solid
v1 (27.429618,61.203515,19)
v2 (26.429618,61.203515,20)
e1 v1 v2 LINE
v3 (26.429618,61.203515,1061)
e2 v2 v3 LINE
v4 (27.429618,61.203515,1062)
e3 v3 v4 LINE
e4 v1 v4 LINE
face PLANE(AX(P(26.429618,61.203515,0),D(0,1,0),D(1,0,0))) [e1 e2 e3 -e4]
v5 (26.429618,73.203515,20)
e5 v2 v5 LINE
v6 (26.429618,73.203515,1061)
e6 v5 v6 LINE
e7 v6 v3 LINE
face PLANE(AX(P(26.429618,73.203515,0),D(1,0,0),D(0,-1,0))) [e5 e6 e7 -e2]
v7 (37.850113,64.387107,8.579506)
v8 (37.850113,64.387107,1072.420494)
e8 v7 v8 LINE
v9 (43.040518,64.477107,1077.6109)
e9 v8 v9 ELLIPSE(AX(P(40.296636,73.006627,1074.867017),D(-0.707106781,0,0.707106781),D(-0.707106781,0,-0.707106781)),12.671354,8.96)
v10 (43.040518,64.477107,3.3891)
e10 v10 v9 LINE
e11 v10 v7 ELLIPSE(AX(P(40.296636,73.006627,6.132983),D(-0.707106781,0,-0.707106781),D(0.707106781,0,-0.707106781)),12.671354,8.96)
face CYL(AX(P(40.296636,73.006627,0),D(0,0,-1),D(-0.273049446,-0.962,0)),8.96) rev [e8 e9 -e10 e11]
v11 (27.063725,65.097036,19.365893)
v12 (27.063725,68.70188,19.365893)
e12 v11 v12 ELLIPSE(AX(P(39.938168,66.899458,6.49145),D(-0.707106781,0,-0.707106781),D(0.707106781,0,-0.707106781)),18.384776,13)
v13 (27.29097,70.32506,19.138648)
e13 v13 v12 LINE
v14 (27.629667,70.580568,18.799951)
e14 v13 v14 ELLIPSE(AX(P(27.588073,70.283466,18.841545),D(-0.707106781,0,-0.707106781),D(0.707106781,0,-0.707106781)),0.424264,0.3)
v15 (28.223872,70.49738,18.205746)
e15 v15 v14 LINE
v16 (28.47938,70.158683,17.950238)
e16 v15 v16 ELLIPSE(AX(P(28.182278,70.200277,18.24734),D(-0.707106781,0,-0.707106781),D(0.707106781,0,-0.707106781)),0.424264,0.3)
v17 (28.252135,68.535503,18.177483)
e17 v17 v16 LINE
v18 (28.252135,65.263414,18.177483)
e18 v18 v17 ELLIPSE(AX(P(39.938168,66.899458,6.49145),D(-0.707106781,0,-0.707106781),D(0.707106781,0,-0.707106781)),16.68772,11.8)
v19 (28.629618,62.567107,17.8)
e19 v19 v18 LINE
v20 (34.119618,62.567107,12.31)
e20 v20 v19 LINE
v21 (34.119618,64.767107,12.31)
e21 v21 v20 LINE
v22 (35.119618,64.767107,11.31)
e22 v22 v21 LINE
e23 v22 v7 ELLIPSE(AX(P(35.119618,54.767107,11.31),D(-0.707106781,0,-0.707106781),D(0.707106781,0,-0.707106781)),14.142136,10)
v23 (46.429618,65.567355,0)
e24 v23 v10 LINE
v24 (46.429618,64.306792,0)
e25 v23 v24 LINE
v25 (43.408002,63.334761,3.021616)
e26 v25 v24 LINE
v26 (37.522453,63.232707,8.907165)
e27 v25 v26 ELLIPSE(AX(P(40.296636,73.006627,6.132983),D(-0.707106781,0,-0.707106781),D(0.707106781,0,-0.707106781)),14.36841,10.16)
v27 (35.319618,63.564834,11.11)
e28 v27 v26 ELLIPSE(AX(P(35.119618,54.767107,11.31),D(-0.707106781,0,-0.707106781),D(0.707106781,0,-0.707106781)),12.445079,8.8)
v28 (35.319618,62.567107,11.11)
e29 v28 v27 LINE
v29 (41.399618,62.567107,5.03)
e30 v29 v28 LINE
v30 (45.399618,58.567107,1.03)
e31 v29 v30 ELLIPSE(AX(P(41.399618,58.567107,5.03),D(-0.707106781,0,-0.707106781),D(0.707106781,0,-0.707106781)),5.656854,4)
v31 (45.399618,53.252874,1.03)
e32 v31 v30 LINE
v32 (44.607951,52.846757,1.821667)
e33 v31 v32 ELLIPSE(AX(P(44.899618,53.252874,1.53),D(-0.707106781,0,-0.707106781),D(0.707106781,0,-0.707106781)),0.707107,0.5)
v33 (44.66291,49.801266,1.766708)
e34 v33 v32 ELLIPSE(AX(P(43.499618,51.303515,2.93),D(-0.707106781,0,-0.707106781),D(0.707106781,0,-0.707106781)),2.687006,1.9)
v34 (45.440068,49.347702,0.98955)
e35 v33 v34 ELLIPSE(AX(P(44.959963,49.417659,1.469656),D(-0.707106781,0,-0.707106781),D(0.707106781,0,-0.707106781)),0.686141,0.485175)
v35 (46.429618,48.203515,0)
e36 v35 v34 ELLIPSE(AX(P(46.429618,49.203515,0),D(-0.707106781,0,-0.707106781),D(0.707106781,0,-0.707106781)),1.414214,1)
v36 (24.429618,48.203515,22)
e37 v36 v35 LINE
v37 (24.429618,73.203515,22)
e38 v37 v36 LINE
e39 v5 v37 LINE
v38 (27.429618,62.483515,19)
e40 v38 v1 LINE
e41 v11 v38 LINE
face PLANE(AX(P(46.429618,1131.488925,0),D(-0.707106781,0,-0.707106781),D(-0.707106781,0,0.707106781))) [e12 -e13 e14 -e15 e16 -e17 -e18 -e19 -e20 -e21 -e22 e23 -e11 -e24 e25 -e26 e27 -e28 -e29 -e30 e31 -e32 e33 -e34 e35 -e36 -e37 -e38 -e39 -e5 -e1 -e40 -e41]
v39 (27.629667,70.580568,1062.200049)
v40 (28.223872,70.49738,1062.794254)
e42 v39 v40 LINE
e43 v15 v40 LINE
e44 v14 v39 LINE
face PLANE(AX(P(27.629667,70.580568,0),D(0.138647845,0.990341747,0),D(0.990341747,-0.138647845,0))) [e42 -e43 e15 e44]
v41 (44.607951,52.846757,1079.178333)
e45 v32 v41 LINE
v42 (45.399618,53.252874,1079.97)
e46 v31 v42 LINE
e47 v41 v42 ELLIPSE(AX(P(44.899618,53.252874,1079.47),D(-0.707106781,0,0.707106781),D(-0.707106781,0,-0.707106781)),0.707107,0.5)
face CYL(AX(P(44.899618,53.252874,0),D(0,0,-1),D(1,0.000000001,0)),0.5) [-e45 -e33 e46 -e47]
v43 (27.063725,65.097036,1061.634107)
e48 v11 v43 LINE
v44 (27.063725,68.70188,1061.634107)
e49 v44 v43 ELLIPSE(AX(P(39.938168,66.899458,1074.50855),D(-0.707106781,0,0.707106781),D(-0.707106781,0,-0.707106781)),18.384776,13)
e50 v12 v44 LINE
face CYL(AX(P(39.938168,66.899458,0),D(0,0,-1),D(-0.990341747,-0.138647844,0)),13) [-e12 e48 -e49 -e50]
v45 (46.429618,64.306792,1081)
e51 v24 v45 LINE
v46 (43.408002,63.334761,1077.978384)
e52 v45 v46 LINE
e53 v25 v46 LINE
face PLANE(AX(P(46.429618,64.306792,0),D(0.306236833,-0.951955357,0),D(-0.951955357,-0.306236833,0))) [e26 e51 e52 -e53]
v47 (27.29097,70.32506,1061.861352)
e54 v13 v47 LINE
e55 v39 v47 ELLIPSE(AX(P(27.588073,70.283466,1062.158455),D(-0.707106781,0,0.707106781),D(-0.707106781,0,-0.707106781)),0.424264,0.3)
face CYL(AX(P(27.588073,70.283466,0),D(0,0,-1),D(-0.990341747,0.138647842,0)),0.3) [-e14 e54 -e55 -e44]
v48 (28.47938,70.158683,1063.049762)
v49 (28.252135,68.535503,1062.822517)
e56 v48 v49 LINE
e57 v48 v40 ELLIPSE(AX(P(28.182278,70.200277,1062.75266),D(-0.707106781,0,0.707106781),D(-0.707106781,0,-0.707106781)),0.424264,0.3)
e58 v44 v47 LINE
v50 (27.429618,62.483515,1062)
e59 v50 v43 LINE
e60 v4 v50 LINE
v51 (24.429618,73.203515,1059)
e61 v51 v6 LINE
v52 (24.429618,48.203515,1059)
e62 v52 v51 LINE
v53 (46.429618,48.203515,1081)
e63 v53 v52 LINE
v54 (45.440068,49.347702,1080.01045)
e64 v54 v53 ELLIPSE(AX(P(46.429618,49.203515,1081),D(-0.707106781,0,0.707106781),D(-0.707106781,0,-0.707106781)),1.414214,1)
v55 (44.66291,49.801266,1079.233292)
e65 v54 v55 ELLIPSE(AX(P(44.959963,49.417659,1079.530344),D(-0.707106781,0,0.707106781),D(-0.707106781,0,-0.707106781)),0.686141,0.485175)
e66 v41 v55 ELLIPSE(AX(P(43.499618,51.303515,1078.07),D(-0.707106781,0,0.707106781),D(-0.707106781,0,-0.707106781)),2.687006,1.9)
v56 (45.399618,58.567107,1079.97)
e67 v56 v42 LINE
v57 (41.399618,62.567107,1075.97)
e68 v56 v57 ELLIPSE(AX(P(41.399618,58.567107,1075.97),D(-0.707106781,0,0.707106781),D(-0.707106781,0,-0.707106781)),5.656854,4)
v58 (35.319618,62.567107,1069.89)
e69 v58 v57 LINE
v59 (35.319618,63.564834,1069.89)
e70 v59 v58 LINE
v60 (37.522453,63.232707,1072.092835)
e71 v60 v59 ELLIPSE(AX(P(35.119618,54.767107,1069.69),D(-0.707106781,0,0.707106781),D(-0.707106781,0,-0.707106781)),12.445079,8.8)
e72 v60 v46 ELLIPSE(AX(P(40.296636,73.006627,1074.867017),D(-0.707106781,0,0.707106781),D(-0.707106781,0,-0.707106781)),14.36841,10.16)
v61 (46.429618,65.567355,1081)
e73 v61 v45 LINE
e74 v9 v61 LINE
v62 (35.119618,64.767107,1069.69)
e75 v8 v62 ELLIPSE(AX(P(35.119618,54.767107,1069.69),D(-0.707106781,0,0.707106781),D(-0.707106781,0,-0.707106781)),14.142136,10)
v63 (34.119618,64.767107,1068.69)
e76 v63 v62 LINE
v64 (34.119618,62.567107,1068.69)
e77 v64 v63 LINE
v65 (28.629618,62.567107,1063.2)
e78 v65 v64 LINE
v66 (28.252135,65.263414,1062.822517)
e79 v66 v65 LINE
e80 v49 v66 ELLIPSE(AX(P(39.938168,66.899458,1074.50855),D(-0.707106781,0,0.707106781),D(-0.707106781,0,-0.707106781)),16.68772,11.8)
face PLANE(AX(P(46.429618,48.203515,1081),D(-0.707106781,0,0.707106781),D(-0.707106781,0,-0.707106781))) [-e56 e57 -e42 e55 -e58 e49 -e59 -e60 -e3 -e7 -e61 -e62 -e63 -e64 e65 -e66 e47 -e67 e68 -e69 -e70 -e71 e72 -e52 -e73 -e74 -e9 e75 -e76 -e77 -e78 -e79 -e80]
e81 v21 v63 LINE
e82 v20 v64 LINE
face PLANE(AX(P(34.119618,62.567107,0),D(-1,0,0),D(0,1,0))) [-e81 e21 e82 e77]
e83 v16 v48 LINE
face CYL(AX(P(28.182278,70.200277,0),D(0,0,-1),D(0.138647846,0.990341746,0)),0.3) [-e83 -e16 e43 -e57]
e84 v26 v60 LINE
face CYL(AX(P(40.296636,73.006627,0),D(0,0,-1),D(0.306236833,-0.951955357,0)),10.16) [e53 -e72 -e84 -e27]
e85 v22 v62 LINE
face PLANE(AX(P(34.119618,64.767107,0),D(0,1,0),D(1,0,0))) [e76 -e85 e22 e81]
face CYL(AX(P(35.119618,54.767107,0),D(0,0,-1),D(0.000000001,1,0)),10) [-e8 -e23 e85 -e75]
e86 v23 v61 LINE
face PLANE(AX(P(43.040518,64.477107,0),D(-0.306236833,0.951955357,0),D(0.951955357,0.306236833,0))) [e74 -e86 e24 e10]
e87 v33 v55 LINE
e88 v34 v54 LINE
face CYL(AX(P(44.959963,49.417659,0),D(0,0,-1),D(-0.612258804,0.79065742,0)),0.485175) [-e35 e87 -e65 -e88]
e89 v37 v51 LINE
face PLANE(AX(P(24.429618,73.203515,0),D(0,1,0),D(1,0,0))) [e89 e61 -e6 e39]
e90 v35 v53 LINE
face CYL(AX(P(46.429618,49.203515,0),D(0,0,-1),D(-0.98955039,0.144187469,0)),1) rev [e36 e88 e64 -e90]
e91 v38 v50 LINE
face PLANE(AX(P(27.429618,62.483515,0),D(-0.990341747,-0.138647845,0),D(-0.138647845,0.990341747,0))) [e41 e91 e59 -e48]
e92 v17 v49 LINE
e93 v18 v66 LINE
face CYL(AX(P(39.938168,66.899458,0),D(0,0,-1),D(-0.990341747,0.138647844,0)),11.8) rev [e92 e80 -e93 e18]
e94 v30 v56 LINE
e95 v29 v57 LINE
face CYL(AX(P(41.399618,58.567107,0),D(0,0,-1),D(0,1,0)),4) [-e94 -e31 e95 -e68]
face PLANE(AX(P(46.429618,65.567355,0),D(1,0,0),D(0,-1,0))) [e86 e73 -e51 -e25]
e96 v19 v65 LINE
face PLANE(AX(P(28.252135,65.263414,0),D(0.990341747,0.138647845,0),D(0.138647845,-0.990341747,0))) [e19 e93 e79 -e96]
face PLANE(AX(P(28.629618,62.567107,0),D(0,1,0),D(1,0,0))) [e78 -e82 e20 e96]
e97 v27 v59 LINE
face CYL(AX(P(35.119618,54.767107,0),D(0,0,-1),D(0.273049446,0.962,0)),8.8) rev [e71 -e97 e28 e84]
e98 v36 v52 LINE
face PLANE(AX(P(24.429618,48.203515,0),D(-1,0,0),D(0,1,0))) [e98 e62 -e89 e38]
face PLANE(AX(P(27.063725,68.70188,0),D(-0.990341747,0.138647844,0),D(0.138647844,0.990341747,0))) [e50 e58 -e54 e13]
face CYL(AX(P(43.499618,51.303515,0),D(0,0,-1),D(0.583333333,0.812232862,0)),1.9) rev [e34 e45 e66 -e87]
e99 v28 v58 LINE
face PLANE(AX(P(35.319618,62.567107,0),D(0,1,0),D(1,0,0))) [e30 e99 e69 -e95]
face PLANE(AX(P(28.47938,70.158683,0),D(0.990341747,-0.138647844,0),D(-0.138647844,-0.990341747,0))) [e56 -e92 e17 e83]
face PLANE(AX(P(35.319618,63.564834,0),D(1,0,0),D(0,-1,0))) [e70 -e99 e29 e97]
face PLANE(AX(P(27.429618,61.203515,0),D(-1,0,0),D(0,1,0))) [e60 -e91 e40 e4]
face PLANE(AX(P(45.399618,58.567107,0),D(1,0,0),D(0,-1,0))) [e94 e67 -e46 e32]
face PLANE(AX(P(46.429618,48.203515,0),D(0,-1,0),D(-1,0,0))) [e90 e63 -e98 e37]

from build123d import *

# Parameters (mm, degrees)
EXTRUDE1_DEPTH      = 1081
EXTRUDE4_DEPTH      = 1083.285410341
EXTRUDE4_DEPTH_BACK = 1083.285410341
EXTRUDE5_DEPTH      = 30


with BuildPart() as part:
    # Sketch2 → Extrude1 (new body)
    with BuildSketch(Plane.XY):
        with BuildLine():
            Line((27.429618111, 61.203514875), (27.429618111, 62.483514875))
            Line((27.429618111, 62.483514875), (27.063725093, 65.097036429))
            ThreePointArc((27.063725093, 65.097036429), (26.9381678, 66.899458408), (27.063725093, 68.701880387))
            Line((27.063725093, 68.701880387), (27.290970266, 70.325060195))
            ThreePointArc((27.290970266, 70.325060195), (27.40740123, 70.522960701), (27.629667144, 70.580568366))
            Line((27.629667144, 70.580568366), (28.223872192, 70.497379659))
            ThreePointArc((28.223872192, 70.497379659), (28.421772697, 70.380948695), (28.479380362, 70.158682782))
            Line((28.479380362, 70.158682782), (28.252135189, 68.535502974))
            ThreePointArc((28.252135189, 68.535502974), (28.1381678, 66.899458408), (28.252135189, 65.263413843))
            Line((28.252135189, 65.263413843), (28.629618111, 62.56710726))
            Line((28.629618111, 62.56710726), (34.119618111, 62.56710726))
            Line((34.119618111, 62.56710726), (34.119618111, 64.76710726))
            Line((34.119618111, 64.76710726), (35.119618111, 64.76710726))
            ThreePointArc((35.119618111, 64.76710726), (36.498022986, 64.671651671), (37.850112572, 64.38710726))
            ThreePointArc((37.850112572, 64.38710726), (40.451975855, 64.047973934), (43.040517634, 64.47710726))
            Line((43.040517634, 64.47710726), (46.429618111, 65.567355231))
            Line((46.429618111, 65.567355231), (46.429618111, 64.306791917))
            Line((46.429618111, 64.306791917), (43.408001834, 63.334760831))
            ThreePointArc((43.408001834, 63.334760831), (40.472780352, 62.848154292), (37.522453236, 63.23270726))
            ThreePointArc((37.522453236, 63.23270726), (36.431587911, 63.468758554), (35.319618111, 63.564834239))
            Line((35.319618111, 63.564834239), (35.319618111, 62.56710726))
            Line((35.319618111, 62.56710726), (41.399618111, 62.56710726))
            ThreePointArc((41.399618111, 62.56710726), (44.228045236, 61.395534384), (45.399618111, 58.56710726))
            Line((45.399618111, 58.56710726), (45.399618111, 53.252873744))
            ThreePointArc((45.399618111, 53.252873744), (45.127835843, 52.807995483), (44.607951444, 52.846757313))
            ThreePointArc((44.607951444, 52.846757313), (41.599927405, 51.269233396), (44.662909839, 49.801265776))
            ThreePointArc((44.662909839, 49.801265776), (45.204517239, 49.836690545), (45.440067721, 49.347702344))
            ThreePointArc((45.440067721, 49.347702344), (45.673249329, 48.549369428), (46.429618111, 48.203514875))
            Line((46.429618111, 48.203514875), (24.429618111, 48.203514875))
            Line((24.429618111, 48.203514875), (24.429618111, 73.203514875))
            Line((24.429618111, 73.203514875), (26.429618111, 73.203514875))
            Line((26.429618111, 73.203514875), (26.429618111, 61.203514875))
            Line((26.429618111, 61.203514875), (27.429618111, 61.203514875))
        make_face()
    extrude(amount=EXTRUDE1_DEPTH)

    # Sketch4 → Extrude4 (cut, two sides: drawn at the far end of the back side and taken through both)
    with BuildSketch(Plane.XZ.offset(-48.203514875).offset(-EXTRUDE4_DEPTH_BACK)):
        Polygon((24.429618111, 0), (46.429618111, 0), (24.429618111, 22), align=None)
    extrude(amount=EXTRUDE4_DEPTH + EXTRUDE4_DEPTH_BACK, mode=Mode.SUBTRACT)

    # Sketch5 → Extrude5 (cut)
    with BuildSketch(Plane.XZ.offset(-48.203514875)):
        Polygon((46.429618111, 1081), (24.429618111, 1059), (24.429618111, 1081), align=None)
    extrude(amount=-EXTRUDE5_DEPTH, mode=Mode.SUBTRACT)


solid = part.part
